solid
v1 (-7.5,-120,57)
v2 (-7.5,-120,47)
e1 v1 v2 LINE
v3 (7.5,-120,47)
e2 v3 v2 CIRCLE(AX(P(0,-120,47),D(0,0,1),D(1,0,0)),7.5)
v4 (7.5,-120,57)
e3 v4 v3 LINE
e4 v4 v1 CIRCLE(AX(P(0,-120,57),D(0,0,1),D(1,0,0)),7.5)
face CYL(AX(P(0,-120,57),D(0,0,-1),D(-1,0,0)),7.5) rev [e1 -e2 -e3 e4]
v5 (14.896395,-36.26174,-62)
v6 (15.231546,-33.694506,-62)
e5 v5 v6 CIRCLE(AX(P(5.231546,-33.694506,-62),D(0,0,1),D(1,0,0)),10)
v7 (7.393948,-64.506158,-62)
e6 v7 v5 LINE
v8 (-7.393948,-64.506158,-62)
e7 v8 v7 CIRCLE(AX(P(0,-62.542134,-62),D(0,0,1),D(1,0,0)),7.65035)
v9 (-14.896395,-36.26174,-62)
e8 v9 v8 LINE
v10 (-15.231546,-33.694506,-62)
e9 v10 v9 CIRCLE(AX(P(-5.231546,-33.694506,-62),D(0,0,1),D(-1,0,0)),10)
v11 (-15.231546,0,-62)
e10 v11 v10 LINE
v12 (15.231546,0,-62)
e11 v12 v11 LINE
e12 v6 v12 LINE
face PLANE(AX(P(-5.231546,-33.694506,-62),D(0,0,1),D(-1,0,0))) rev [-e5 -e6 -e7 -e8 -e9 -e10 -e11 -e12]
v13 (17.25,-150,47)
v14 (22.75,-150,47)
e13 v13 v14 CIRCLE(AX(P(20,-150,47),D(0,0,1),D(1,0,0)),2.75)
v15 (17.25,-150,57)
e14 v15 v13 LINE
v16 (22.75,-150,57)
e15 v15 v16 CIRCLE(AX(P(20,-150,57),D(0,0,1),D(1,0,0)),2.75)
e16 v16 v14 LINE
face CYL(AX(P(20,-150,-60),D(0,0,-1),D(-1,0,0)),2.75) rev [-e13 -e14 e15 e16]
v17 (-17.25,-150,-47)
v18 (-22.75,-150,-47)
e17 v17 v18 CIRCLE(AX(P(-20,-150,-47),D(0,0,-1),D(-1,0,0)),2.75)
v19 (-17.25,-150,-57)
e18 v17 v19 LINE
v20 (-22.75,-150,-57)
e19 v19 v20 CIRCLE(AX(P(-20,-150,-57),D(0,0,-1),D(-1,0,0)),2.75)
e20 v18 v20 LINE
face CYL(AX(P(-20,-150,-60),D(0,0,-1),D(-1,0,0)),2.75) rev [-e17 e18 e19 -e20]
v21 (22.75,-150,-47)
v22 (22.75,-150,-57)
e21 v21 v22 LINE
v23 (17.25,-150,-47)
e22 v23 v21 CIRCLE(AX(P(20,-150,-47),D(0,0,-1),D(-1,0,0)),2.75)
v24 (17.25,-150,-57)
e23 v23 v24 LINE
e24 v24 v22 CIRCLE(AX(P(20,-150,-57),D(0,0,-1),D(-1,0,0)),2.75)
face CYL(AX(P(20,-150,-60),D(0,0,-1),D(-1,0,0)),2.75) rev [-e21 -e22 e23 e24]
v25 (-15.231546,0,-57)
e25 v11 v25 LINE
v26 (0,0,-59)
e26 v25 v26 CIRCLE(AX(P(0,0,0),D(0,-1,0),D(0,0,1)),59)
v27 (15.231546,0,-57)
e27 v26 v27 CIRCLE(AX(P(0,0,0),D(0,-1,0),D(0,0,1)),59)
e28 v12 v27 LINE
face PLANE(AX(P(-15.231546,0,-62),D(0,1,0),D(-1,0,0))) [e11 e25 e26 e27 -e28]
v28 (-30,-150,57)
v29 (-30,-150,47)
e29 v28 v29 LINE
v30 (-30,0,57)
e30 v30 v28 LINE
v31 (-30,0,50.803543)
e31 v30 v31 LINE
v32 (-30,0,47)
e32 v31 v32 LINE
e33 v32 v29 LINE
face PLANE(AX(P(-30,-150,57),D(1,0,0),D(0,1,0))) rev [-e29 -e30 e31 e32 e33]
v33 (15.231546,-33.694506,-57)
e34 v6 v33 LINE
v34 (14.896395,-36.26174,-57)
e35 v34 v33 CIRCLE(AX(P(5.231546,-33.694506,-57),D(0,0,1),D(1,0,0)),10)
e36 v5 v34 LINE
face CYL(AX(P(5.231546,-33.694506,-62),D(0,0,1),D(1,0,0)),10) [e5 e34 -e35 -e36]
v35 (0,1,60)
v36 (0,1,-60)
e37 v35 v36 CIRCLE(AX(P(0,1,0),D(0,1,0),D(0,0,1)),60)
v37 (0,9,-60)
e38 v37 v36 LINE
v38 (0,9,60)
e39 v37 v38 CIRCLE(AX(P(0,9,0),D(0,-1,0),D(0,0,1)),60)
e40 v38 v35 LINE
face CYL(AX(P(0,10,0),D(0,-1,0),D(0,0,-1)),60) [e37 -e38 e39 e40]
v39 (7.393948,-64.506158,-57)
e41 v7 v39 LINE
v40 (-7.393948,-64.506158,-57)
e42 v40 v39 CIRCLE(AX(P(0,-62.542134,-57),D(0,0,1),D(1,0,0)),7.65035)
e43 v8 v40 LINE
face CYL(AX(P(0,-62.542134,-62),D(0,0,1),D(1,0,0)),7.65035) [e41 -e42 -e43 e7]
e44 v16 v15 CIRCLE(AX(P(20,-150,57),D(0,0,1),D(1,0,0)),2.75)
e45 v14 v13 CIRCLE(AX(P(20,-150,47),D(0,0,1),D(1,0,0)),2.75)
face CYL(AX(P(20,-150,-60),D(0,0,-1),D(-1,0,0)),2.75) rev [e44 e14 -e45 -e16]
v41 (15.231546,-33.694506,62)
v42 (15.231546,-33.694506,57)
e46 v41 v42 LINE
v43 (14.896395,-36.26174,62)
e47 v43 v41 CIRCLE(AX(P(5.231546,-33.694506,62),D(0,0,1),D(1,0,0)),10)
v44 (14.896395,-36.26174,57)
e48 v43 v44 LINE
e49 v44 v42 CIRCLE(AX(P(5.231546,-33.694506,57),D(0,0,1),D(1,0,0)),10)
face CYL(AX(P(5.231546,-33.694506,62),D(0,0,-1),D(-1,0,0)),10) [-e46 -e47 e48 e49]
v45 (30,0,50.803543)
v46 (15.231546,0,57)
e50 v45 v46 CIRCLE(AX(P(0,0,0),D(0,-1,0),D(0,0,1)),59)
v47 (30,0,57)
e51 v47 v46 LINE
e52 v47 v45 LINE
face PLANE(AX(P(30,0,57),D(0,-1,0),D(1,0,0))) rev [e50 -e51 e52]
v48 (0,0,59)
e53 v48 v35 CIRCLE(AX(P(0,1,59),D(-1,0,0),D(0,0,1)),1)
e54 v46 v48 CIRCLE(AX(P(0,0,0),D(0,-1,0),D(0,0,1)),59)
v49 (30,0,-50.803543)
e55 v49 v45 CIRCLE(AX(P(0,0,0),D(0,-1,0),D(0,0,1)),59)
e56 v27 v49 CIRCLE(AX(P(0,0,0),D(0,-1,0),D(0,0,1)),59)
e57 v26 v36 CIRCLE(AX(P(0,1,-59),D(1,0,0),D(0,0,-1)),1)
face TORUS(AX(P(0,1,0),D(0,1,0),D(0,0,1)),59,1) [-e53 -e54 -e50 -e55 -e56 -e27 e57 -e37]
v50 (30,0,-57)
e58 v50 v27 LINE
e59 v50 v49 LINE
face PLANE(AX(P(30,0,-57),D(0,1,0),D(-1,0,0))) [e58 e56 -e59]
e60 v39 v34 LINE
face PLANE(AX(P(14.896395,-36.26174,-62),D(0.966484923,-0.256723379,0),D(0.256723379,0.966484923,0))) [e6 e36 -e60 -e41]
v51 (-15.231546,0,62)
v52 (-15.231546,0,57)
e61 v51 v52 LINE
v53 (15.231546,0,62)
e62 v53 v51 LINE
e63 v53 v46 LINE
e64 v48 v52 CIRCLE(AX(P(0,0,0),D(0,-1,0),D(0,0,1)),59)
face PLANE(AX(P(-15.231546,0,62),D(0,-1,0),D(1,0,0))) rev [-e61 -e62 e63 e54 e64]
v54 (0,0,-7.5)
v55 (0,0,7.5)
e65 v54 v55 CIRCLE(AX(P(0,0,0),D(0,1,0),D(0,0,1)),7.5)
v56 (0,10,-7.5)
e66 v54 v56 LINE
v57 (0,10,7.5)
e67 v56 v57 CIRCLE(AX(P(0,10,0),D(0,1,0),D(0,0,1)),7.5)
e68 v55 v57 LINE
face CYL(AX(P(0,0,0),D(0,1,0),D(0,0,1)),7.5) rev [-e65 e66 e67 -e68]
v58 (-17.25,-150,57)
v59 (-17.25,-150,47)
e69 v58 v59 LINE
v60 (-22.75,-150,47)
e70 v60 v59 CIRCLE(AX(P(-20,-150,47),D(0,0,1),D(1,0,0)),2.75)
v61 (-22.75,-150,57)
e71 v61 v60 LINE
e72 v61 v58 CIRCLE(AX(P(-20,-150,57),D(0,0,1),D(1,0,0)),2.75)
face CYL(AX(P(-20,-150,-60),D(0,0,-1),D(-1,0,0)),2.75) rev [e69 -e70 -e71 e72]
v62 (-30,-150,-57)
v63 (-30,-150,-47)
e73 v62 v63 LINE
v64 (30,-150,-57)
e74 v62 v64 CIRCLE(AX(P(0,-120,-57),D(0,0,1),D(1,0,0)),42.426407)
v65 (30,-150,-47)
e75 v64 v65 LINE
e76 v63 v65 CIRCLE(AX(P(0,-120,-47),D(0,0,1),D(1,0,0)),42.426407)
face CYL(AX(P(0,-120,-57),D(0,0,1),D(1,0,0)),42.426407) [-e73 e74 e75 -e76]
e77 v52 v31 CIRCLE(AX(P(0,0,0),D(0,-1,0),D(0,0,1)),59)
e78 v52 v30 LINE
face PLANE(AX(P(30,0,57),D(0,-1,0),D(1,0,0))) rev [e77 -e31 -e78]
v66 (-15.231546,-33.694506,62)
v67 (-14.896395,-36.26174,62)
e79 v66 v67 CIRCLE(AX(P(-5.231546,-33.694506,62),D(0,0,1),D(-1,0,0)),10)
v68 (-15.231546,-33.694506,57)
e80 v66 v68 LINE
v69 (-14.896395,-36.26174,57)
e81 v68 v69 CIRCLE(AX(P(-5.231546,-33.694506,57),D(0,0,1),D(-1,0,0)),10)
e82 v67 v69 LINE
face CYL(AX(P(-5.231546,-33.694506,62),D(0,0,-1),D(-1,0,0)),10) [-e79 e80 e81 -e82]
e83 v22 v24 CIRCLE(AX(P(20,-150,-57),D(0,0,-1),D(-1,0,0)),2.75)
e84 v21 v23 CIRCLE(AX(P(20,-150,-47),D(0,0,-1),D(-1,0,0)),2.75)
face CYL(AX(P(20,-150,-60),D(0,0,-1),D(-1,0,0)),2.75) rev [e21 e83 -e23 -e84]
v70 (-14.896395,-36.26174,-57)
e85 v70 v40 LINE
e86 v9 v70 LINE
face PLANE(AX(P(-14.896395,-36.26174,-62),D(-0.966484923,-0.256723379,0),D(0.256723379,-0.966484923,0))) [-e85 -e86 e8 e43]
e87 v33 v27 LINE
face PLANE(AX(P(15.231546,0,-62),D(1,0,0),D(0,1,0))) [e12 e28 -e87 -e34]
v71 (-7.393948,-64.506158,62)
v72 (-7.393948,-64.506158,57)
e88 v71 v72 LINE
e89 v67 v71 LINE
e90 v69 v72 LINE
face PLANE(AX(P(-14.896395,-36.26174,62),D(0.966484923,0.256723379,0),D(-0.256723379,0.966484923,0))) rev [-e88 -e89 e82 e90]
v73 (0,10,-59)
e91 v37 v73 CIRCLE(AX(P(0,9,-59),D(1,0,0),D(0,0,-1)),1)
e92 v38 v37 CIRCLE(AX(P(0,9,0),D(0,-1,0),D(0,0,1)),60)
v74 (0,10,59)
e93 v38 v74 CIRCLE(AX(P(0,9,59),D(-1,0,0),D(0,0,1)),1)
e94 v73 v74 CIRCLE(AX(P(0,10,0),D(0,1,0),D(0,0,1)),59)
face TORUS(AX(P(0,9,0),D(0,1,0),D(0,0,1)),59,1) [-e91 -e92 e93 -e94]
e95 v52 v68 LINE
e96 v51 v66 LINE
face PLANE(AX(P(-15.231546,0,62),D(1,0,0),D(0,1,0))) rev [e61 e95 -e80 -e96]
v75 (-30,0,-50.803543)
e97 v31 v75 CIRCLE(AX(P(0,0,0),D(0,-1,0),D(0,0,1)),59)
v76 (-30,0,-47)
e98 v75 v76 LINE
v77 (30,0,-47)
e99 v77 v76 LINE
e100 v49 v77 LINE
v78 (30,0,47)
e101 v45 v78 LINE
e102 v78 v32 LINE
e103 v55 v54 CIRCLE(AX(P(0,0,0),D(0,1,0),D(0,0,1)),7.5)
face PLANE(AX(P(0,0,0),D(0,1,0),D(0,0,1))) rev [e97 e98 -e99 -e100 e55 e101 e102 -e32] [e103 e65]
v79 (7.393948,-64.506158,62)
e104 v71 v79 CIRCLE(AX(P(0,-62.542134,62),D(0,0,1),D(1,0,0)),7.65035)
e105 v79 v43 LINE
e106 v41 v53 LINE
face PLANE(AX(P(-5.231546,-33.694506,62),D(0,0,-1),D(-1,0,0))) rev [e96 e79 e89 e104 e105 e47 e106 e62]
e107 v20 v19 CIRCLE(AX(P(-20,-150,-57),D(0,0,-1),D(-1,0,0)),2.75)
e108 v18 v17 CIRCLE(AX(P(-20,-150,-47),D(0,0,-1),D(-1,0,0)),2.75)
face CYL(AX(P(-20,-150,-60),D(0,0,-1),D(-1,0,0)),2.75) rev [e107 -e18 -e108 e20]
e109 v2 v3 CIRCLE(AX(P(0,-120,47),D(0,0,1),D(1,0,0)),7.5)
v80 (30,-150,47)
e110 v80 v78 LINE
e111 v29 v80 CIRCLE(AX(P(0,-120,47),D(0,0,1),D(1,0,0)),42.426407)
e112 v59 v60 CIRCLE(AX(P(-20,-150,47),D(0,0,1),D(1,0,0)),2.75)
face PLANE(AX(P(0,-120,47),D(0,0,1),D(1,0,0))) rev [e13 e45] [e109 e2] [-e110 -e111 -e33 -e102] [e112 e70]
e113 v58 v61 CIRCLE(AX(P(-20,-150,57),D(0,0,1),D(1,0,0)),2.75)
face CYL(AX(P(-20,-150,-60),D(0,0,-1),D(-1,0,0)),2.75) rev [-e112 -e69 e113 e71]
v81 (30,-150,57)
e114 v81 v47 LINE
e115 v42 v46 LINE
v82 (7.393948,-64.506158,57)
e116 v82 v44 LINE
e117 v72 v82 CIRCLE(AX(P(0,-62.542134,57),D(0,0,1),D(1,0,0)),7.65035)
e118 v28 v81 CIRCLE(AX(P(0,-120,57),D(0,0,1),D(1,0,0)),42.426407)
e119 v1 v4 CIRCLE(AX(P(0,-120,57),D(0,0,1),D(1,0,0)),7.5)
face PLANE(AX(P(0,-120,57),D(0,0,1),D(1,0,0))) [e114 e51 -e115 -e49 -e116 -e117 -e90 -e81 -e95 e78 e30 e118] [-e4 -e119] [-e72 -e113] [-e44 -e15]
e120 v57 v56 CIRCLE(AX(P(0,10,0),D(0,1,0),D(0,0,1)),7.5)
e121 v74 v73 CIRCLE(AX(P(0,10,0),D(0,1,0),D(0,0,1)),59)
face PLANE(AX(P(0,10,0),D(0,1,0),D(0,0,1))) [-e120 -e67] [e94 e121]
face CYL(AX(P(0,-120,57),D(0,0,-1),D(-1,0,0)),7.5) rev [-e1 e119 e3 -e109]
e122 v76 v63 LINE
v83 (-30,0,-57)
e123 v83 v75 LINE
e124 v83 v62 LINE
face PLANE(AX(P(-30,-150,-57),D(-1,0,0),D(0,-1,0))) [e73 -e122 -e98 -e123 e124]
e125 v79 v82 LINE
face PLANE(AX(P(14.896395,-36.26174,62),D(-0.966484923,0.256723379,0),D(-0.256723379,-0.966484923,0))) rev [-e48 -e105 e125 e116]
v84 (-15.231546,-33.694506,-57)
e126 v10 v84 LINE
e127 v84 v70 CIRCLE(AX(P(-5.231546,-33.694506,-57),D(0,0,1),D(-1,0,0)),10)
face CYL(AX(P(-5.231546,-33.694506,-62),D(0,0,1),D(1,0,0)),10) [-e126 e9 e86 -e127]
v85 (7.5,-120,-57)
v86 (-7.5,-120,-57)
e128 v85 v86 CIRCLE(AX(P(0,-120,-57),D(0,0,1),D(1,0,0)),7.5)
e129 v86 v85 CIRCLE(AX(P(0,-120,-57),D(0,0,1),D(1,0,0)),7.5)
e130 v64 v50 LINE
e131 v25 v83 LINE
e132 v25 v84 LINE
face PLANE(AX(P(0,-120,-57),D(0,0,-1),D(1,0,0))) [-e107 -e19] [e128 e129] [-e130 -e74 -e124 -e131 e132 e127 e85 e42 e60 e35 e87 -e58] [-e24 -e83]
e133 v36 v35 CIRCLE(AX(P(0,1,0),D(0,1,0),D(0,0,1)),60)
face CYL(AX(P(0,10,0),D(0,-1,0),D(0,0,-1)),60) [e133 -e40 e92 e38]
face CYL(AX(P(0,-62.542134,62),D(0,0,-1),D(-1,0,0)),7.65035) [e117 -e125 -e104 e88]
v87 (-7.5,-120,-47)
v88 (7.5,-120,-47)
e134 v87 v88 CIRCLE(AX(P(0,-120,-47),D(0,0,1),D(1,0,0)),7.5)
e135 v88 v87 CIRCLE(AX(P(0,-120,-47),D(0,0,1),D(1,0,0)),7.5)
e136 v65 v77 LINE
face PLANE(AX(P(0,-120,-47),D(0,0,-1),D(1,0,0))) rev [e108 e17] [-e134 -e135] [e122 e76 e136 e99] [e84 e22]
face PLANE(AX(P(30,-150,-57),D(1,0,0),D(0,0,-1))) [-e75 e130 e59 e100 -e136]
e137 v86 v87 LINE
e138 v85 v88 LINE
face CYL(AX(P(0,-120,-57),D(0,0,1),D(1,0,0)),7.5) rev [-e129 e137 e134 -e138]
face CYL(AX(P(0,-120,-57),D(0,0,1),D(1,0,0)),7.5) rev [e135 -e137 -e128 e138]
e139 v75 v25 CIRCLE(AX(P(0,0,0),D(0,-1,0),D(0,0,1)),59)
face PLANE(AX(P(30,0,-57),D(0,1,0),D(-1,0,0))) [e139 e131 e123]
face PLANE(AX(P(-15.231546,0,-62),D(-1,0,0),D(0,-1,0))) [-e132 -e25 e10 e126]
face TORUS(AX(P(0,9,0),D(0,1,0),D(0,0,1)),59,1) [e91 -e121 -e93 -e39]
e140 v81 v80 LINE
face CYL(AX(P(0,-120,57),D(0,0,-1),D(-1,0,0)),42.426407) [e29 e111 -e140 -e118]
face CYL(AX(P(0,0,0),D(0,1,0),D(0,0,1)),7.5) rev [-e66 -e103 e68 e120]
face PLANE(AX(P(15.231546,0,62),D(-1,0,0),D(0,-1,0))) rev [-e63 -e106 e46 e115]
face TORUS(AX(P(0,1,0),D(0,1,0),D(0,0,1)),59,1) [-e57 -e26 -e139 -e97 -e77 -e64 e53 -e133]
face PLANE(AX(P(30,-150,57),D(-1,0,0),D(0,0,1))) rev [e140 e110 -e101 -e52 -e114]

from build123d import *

# Parameters (mm, degrees)
SKETCH1_R           = 60
BOSS_EXTRUDE1_DEPTH = 10
FILLET2_R           = 1
SKETCH5_R           = 7.5
CUT_EXTRUDE2_DEPTH  = 86.440037535
SKETCH2_R           = 7.5
BOSS_EXTRUDE2_DEPTH = 10
BOSS_EXTRUDE4_DEPTH = 5


with BuildPart() as part:
    # Sketch1 → Boss-Extrude1 (new body)
    with BuildSketch(Plane(origin=(0, 0, 0), x_dir=(1, 0, 0), z_dir=(0, 1, 0))):
        with Locations(Location((0, 0, 0), (0, 0, 270))):
            Circle(SKETCH1_R)
    extrude(amount=BOSS_EXTRUDE1_DEPTH)

    # Fillet2
    fillet2_edges = [part.edges().sort_by_distance(p)[0] for p in [
        (0, 0, -60),
        (0, 10, -60),
    ]]
    fillet(fillet2_edges, radius=FILLET2_R)

    # Sketch5 → Cut-Extrude2 (cut, through all)
    with BuildSketch(Plane(origin=(0, 10, 0), x_dir=(1, 0, 0), z_dir=(0, 1, 0))):
        with Locations(Location((0, 0, 0), (0, 0, 270))):
            Circle(SKETCH5_R)
    cut_extrude2 = extrude(amount=-CUT_EXTRUDE2_DEPTH, mode=Mode.SUBTRACT)

    # Sketch2 → Boss-Extrude2 (add)
    with BuildSketch(Plane.XY.offset(47)):
        with BuildLine():
            Line((30, 0), (-30, 0))
            Line((-30, 0), (-30, -150))
            ThreePointArc((-30, -150), (0, -162.426406871), (30, -150))
            Line((30, -150), (30, 0))
        make_face()
        with Locations((0, -120)):
            Circle(SKETCH2_R, mode=Mode.SUBTRACT)
    boss_extrude2 = extrude(amount=BOSS_EXTRUDE2_DEPTH)

    # Sketch7 → Boss-Extrude4 (add)
    with BuildSketch(Plane.XY.offset(57)):
        with BuildLine():
            Line((-15.231546212, 0), (15.231546212, 0))
            Line((15.231546212, 0), (15.231546212, -33.694506244))
            ThreePointArc((15.231546212, -33.694506244), (15.147404529, -34.989015356), (14.896395444, -36.261740032))
            Line((14.896395444, -36.261740032), (7.393947913, -64.506158047))
            ThreePointArc((7.393947913, -64.506158047), (0, -70.192484331), (-7.393947913, -64.506158047))
            Line((-7.393947913, -64.506158047), (-14.896395444, -36.261740032))
            ThreePointArc((-14.896395444, -36.261740032), (-15.147404529, -34.989015356), (-15.231546212, -33.694506244))
            Line((-15.231546212, -33.694506244), (-15.231546212, 0))
        make_face()
    boss_extrude4 = extrude(amount=BOSS_EXTRUDE4_DEPTH)

    # Mirror2: Cut-Extrude2, Boss-Extrude2, Boss-Extrude4 across plane
    add(cut_extrude2.mirror(Plane.XY), mode=Mode.SUBTRACT)
    add(boss_extrude2.mirror(Plane.XY))
    add(boss_extrude4.mirror(Plane.XY))

    # Sketch10 → CBORE for M5 Hexagon head bolts-Full thread-grade C1 (revolve, cut)
    with BuildSketch(Plane(origin=(20, -150, -60), x_dir=(0, 1, 0), z_dir=(1, 0, 0))):
        Polygon((0, 0), (0, 122), (2.75, 122), (2.75, 0.5), (5.5, 0.5), (5.5, 0.025), (5.525, 0), align=None)
    cbore_for_m5_hexagon_head_bolts_full_thr = revolve(axis=Axis((20, -150, -66.35), (0, 0, 1)), mode=Mode.SUBTRACT)

    # Mirror3: CBORE for M5 Hexagon head bolts-Full thread-grade C1 across plane
    add(cbore_for_m5_hexagon_head_bolts_full_thr.mirror(Plane.ZY), mode=Mode.SUBTRACT)


solid = part.part
